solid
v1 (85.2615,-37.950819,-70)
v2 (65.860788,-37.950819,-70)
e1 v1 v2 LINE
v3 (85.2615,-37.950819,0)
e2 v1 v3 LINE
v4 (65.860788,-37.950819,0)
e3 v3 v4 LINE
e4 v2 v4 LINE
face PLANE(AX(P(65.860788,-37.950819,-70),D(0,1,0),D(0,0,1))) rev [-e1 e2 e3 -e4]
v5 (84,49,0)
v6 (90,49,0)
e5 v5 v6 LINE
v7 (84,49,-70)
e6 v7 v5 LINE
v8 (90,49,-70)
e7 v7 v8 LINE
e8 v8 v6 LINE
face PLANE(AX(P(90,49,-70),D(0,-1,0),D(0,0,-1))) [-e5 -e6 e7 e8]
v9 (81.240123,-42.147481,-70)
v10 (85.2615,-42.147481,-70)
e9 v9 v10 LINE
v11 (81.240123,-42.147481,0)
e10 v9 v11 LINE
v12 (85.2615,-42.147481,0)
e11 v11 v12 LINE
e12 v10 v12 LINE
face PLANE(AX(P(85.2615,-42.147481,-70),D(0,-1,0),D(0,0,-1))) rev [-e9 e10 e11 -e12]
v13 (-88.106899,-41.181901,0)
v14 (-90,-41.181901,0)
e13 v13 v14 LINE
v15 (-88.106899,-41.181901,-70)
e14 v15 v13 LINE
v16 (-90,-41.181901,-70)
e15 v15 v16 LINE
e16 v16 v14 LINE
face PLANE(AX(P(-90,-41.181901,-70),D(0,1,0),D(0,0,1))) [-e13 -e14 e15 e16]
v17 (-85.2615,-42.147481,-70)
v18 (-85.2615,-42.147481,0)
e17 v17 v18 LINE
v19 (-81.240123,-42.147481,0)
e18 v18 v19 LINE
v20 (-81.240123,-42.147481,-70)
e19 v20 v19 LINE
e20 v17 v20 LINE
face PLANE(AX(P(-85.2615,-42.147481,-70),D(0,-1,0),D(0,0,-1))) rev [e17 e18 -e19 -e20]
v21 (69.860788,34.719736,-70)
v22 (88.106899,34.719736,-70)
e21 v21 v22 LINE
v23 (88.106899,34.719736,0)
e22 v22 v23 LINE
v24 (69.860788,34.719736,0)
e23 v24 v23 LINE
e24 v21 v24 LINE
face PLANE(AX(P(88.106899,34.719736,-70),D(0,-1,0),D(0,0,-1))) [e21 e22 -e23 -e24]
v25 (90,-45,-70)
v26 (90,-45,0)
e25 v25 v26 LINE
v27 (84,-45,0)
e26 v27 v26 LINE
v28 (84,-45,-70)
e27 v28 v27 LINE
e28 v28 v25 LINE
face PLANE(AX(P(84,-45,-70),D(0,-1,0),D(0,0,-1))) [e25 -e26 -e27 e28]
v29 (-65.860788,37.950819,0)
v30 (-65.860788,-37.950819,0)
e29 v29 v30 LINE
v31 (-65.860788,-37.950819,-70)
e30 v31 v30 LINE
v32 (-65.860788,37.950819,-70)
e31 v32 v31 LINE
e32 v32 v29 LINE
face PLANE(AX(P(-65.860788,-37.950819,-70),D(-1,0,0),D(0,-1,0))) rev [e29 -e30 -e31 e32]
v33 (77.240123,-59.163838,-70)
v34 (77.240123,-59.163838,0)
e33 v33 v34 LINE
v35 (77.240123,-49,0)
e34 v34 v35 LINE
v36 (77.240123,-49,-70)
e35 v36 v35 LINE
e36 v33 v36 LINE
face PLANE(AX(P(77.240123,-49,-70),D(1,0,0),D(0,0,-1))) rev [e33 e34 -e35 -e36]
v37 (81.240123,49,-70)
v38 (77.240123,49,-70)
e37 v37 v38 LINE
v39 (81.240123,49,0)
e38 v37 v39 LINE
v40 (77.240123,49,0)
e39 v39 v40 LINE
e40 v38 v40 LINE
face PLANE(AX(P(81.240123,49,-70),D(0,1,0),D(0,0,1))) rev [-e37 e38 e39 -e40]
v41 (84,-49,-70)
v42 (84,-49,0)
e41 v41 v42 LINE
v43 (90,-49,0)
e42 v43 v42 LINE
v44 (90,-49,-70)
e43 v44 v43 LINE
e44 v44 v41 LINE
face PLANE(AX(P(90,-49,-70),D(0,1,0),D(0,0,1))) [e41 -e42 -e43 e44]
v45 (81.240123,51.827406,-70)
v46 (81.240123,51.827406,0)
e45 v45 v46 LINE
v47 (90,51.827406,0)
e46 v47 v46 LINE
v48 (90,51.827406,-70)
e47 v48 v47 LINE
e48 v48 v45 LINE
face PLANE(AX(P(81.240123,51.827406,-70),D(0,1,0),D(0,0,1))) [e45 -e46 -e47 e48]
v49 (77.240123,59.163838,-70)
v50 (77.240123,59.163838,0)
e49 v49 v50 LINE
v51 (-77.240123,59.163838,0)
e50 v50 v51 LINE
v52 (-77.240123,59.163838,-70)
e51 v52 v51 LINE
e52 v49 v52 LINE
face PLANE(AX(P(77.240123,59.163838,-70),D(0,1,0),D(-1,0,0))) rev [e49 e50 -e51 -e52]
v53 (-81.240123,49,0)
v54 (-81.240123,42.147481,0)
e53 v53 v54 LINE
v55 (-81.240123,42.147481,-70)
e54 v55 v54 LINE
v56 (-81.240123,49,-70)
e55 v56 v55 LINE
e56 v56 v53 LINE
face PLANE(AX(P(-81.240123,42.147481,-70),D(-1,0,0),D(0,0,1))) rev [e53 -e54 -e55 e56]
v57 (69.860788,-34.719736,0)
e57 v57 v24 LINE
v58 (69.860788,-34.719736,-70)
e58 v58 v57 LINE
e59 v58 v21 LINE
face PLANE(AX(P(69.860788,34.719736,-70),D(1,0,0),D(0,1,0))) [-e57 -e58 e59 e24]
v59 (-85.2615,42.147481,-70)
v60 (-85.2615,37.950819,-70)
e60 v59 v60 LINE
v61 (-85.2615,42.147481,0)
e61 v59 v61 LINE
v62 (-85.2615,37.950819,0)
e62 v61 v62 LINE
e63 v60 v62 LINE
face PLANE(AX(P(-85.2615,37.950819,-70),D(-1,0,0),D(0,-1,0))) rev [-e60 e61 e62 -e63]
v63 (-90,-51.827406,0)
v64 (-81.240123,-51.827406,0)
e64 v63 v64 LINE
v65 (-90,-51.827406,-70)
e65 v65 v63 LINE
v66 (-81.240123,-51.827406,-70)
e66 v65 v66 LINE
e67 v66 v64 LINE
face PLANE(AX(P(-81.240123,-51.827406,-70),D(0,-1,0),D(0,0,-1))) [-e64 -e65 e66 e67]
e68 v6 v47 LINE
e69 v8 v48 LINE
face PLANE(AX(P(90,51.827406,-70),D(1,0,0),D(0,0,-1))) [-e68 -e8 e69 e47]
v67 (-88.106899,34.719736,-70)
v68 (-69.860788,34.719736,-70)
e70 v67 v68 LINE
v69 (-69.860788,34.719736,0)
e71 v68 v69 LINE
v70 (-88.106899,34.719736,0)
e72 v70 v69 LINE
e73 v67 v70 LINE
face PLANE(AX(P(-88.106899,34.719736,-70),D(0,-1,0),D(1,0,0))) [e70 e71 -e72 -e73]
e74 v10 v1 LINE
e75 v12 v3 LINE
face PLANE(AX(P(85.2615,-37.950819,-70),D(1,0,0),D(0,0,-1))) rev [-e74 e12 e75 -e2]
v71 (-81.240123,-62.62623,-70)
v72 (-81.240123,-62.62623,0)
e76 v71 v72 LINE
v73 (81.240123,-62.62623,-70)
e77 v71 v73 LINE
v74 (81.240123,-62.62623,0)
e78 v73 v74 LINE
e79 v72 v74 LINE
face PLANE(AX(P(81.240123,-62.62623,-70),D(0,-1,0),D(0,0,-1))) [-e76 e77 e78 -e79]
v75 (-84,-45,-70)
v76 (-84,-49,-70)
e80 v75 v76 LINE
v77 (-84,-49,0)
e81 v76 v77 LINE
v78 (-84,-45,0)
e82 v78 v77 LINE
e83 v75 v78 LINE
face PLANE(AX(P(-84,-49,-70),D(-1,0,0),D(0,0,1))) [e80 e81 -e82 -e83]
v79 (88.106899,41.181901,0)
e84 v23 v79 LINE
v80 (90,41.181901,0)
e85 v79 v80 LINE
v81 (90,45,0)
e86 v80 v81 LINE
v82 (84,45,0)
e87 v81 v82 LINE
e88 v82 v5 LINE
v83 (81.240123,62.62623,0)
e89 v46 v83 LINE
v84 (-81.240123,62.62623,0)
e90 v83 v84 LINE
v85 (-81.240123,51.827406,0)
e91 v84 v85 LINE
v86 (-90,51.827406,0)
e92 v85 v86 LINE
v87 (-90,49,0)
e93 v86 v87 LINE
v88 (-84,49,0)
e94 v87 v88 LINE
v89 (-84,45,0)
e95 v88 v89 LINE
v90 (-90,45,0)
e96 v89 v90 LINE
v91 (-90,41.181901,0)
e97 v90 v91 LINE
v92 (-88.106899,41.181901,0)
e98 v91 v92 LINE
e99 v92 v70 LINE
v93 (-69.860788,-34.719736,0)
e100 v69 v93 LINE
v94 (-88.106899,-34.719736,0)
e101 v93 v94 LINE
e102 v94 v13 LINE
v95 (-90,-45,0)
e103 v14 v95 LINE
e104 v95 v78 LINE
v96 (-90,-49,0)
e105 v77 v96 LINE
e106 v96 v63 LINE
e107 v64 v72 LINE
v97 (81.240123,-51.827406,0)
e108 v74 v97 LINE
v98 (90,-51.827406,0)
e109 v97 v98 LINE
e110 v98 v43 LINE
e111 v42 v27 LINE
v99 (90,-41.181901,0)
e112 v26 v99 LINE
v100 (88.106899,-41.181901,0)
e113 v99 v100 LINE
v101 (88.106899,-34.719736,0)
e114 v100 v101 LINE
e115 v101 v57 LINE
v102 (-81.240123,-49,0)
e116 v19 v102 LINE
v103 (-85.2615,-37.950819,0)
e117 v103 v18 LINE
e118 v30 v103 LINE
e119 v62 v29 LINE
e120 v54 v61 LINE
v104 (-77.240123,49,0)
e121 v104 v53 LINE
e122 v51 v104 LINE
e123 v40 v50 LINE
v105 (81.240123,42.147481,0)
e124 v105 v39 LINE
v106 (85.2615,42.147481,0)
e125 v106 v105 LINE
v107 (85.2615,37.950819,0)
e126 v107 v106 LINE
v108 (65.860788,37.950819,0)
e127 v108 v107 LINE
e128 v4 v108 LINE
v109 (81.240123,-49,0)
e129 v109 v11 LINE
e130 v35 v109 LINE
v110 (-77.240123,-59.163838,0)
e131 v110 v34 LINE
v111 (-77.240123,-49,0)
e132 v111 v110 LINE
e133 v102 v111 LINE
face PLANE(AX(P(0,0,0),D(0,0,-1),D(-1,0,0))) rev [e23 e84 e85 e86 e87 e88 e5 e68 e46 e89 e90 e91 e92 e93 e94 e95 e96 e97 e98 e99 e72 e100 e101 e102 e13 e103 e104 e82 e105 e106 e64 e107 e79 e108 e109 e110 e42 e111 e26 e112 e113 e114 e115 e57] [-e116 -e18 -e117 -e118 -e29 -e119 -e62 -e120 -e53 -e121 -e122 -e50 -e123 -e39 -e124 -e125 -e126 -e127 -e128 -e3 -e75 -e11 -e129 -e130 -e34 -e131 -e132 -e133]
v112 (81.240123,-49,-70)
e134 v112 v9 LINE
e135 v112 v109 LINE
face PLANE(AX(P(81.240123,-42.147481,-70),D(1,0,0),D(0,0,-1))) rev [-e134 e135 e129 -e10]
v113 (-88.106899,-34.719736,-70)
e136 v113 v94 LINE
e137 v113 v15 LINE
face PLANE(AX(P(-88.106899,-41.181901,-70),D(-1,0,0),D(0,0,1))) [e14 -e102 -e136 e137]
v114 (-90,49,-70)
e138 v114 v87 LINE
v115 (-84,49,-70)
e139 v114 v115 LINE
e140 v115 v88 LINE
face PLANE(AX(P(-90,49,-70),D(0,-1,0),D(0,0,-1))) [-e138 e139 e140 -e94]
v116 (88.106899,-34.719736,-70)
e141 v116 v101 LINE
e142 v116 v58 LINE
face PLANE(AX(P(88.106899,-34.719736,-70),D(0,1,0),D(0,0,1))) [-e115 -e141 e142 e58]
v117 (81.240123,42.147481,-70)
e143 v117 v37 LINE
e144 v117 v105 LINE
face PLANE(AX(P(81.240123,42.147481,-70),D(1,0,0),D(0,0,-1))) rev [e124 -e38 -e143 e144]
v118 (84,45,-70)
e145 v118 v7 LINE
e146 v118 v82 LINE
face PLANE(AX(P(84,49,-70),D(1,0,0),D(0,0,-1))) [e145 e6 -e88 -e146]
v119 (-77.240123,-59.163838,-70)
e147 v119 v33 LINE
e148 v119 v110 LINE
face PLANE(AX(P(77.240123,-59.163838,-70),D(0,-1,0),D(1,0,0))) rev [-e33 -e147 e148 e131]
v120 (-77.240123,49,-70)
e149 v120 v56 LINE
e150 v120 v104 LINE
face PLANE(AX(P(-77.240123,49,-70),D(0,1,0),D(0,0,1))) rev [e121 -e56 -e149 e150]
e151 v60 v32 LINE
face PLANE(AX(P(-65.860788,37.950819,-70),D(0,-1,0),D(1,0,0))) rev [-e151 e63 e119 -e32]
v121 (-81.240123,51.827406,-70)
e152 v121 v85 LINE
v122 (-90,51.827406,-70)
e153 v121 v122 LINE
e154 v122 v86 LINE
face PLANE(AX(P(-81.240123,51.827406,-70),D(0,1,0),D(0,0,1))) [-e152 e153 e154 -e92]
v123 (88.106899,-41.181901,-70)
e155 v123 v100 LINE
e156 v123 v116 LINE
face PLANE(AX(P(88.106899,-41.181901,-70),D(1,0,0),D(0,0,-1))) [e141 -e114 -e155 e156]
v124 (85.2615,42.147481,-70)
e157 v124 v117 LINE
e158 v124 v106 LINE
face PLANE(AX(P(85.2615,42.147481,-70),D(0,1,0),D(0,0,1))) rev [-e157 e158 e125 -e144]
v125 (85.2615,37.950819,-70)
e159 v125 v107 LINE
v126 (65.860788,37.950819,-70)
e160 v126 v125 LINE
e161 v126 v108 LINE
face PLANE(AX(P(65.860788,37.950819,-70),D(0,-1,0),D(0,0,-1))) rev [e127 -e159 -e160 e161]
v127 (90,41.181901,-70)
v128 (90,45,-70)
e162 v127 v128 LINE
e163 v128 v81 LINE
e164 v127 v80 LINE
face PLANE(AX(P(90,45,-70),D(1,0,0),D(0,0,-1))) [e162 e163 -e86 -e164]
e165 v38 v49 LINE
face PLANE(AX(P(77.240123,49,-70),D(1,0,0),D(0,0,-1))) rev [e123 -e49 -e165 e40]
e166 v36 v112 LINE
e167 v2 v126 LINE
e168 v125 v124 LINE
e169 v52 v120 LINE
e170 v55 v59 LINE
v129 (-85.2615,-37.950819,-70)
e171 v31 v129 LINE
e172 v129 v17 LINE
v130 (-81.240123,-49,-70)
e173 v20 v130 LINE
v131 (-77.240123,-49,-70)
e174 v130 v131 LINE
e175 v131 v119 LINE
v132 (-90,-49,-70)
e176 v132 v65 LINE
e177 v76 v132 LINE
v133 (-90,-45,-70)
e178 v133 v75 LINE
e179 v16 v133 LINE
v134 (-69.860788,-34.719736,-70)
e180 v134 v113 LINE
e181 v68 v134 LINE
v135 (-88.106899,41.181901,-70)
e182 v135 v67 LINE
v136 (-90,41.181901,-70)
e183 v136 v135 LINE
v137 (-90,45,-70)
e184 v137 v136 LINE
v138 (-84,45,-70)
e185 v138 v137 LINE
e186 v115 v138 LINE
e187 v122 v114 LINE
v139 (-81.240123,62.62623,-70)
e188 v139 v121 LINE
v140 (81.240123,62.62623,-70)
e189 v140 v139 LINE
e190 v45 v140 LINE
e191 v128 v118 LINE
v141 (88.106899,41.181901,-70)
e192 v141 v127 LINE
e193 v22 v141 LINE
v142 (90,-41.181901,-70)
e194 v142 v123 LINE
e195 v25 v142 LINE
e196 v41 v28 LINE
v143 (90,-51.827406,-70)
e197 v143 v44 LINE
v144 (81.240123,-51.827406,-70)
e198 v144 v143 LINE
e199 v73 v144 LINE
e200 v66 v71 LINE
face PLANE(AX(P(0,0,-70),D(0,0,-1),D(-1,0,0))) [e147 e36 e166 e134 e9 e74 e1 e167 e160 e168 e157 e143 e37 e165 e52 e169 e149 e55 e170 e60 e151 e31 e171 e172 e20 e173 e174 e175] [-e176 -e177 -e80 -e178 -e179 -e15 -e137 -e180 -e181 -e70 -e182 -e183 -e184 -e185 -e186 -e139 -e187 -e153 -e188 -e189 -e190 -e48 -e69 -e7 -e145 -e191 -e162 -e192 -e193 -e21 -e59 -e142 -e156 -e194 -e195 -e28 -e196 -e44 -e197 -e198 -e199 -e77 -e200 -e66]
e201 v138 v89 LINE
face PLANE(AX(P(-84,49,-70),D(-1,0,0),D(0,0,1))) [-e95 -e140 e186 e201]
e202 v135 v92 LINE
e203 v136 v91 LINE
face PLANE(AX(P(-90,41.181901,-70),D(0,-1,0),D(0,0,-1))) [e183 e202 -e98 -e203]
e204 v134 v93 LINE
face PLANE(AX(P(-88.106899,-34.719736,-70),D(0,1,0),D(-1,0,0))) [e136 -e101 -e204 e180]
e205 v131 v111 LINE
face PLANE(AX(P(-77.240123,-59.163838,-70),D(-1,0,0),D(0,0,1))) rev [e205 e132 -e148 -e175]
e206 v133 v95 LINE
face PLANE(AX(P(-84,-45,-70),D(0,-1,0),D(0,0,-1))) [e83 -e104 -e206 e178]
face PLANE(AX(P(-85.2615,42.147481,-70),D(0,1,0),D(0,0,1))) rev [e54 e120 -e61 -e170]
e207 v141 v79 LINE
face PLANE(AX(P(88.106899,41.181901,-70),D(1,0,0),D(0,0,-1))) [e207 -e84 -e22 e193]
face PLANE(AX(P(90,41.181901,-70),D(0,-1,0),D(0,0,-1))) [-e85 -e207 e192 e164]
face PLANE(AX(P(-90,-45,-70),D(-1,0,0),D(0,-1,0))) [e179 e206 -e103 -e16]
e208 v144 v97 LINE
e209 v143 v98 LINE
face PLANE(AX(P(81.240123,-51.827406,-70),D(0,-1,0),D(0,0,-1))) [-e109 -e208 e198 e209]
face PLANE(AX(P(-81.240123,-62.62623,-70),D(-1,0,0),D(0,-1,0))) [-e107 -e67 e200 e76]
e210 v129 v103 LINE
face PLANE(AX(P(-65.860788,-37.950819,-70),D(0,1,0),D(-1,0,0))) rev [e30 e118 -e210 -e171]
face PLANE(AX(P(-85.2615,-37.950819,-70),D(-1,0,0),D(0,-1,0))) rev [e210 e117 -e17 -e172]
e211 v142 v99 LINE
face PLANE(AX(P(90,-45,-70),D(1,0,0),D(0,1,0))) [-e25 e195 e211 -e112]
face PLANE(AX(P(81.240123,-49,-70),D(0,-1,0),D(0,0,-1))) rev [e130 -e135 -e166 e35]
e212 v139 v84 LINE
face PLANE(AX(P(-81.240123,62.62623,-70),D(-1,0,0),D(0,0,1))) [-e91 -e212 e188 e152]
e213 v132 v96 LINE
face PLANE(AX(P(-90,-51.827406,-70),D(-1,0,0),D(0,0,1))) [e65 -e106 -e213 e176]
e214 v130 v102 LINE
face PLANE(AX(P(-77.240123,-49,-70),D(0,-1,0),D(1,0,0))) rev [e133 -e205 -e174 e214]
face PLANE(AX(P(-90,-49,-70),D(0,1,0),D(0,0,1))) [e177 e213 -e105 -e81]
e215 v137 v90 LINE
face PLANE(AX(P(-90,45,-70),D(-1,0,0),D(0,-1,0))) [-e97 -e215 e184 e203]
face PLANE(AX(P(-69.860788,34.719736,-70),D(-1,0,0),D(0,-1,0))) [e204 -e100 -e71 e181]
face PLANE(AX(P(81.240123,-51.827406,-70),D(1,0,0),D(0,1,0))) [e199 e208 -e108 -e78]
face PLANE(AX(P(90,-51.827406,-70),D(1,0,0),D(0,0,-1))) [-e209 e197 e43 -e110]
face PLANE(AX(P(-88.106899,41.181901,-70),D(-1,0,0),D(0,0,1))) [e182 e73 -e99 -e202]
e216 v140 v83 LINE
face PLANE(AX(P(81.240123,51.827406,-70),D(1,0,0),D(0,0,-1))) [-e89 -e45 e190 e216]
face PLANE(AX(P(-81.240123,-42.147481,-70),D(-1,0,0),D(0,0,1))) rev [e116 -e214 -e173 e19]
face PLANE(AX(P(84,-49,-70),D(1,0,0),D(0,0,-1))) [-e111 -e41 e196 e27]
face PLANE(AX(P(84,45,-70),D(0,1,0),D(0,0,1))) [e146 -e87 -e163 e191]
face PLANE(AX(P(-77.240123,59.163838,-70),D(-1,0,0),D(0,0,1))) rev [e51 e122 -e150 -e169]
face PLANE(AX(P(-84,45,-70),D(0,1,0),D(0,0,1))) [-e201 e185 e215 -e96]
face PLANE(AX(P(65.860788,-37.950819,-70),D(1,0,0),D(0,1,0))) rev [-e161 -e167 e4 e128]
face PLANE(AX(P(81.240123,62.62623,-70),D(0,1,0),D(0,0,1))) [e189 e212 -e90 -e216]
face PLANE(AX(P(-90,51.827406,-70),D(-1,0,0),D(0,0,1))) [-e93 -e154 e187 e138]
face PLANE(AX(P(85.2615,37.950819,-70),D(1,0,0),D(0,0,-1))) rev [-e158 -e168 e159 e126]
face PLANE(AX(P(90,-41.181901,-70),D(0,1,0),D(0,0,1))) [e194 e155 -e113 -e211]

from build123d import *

# Parameters (mm, degrees)
BOSS_EXTRUDE1_START = -70
BOSS_EXTRUDE1_DEPTH = 70


with BuildPart() as part:
    # Sketch1 → Boss-Extrude1 (new body)
    with BuildSketch(Plane.XY.offset(BOSS_EXTRUDE1_START)):
        Polygon((90, 49), (84, 49), (84, 45), (90, 45), (90, 41.181900725), (88.106898586, 41.181900725), (88.106898586, 34.71973643), (69.860787635, 34.71973643), (69.860787635, -34.71973643), (88.106898586, -34.71973643), (88.106898586, -41.181900725), (90, -41.181900725), (90, -45), (84, -45), (84, -49), (90, -49), (90, -51.82740617), (81.240122505, -51.82740617), (81.240122505, -62.626229996), (-81.240122505, -62.626229996), (-81.240122505, -51.82740617), (-90, -51.82740617), (-90, -49), (-84, -49), (-84, -45), (-90, -45), (-90, -41.181900725), (-88.106898586, -41.181900725), (-88.106898586, -34.71973643), (-69.860787635, -34.71973643), (-69.860787635, 34.71973643), (-88.106898586, 34.71973643), (-88.106898586, 41.181900725), (-90, 41.181900725), (-90, 45), (-84, 45), (-84, 49), (-90, 49), (-90, 51.82740617), (-81.240122505, 51.82740617), (-81.240122505, 62.626229996), (81.240122505, 62.626229996), (81.240122505, 51.82740617), (90, 51.82740617), align=None)
        Polygon((65.860787635, -37.950818577), (65.860787635, 37.950818577), (85.261500452, 37.950818577), (85.261500452, 42.147480982), (81.240122505, 42.147480982), (81.240122505, 49), (77.240122505, 49), (77.240122505, 59.163837684), (-77.240122505, 59.163837684), (-77.240122505, 49), (-81.240122505, 49), (-81.240122505, 42.147480982), (-85.261500452, 42.147480982), (-85.261500452, 37.950818577), (-65.860787635, 37.950818577), (-65.860787635, -37.950818577), (-85.261500452, -37.950818577), (-85.261500452, -42.147480982), (-81.240122505, -42.147480982), (-81.240122505, -49), (-77.240122505, -49), (-77.240122505, -59.163837684), (77.240122505, -59.163837684), (77.240122505, -49), (81.240122505, -49), (81.240122505, -42.147480982), (85.261500452, -42.147480982), (85.261500452, -37.950818577), align=None, mode=Mode.SUBTRACT)
    extrude(amount=BOSS_EXTRUDE1_DEPTH)


solid = part.part
